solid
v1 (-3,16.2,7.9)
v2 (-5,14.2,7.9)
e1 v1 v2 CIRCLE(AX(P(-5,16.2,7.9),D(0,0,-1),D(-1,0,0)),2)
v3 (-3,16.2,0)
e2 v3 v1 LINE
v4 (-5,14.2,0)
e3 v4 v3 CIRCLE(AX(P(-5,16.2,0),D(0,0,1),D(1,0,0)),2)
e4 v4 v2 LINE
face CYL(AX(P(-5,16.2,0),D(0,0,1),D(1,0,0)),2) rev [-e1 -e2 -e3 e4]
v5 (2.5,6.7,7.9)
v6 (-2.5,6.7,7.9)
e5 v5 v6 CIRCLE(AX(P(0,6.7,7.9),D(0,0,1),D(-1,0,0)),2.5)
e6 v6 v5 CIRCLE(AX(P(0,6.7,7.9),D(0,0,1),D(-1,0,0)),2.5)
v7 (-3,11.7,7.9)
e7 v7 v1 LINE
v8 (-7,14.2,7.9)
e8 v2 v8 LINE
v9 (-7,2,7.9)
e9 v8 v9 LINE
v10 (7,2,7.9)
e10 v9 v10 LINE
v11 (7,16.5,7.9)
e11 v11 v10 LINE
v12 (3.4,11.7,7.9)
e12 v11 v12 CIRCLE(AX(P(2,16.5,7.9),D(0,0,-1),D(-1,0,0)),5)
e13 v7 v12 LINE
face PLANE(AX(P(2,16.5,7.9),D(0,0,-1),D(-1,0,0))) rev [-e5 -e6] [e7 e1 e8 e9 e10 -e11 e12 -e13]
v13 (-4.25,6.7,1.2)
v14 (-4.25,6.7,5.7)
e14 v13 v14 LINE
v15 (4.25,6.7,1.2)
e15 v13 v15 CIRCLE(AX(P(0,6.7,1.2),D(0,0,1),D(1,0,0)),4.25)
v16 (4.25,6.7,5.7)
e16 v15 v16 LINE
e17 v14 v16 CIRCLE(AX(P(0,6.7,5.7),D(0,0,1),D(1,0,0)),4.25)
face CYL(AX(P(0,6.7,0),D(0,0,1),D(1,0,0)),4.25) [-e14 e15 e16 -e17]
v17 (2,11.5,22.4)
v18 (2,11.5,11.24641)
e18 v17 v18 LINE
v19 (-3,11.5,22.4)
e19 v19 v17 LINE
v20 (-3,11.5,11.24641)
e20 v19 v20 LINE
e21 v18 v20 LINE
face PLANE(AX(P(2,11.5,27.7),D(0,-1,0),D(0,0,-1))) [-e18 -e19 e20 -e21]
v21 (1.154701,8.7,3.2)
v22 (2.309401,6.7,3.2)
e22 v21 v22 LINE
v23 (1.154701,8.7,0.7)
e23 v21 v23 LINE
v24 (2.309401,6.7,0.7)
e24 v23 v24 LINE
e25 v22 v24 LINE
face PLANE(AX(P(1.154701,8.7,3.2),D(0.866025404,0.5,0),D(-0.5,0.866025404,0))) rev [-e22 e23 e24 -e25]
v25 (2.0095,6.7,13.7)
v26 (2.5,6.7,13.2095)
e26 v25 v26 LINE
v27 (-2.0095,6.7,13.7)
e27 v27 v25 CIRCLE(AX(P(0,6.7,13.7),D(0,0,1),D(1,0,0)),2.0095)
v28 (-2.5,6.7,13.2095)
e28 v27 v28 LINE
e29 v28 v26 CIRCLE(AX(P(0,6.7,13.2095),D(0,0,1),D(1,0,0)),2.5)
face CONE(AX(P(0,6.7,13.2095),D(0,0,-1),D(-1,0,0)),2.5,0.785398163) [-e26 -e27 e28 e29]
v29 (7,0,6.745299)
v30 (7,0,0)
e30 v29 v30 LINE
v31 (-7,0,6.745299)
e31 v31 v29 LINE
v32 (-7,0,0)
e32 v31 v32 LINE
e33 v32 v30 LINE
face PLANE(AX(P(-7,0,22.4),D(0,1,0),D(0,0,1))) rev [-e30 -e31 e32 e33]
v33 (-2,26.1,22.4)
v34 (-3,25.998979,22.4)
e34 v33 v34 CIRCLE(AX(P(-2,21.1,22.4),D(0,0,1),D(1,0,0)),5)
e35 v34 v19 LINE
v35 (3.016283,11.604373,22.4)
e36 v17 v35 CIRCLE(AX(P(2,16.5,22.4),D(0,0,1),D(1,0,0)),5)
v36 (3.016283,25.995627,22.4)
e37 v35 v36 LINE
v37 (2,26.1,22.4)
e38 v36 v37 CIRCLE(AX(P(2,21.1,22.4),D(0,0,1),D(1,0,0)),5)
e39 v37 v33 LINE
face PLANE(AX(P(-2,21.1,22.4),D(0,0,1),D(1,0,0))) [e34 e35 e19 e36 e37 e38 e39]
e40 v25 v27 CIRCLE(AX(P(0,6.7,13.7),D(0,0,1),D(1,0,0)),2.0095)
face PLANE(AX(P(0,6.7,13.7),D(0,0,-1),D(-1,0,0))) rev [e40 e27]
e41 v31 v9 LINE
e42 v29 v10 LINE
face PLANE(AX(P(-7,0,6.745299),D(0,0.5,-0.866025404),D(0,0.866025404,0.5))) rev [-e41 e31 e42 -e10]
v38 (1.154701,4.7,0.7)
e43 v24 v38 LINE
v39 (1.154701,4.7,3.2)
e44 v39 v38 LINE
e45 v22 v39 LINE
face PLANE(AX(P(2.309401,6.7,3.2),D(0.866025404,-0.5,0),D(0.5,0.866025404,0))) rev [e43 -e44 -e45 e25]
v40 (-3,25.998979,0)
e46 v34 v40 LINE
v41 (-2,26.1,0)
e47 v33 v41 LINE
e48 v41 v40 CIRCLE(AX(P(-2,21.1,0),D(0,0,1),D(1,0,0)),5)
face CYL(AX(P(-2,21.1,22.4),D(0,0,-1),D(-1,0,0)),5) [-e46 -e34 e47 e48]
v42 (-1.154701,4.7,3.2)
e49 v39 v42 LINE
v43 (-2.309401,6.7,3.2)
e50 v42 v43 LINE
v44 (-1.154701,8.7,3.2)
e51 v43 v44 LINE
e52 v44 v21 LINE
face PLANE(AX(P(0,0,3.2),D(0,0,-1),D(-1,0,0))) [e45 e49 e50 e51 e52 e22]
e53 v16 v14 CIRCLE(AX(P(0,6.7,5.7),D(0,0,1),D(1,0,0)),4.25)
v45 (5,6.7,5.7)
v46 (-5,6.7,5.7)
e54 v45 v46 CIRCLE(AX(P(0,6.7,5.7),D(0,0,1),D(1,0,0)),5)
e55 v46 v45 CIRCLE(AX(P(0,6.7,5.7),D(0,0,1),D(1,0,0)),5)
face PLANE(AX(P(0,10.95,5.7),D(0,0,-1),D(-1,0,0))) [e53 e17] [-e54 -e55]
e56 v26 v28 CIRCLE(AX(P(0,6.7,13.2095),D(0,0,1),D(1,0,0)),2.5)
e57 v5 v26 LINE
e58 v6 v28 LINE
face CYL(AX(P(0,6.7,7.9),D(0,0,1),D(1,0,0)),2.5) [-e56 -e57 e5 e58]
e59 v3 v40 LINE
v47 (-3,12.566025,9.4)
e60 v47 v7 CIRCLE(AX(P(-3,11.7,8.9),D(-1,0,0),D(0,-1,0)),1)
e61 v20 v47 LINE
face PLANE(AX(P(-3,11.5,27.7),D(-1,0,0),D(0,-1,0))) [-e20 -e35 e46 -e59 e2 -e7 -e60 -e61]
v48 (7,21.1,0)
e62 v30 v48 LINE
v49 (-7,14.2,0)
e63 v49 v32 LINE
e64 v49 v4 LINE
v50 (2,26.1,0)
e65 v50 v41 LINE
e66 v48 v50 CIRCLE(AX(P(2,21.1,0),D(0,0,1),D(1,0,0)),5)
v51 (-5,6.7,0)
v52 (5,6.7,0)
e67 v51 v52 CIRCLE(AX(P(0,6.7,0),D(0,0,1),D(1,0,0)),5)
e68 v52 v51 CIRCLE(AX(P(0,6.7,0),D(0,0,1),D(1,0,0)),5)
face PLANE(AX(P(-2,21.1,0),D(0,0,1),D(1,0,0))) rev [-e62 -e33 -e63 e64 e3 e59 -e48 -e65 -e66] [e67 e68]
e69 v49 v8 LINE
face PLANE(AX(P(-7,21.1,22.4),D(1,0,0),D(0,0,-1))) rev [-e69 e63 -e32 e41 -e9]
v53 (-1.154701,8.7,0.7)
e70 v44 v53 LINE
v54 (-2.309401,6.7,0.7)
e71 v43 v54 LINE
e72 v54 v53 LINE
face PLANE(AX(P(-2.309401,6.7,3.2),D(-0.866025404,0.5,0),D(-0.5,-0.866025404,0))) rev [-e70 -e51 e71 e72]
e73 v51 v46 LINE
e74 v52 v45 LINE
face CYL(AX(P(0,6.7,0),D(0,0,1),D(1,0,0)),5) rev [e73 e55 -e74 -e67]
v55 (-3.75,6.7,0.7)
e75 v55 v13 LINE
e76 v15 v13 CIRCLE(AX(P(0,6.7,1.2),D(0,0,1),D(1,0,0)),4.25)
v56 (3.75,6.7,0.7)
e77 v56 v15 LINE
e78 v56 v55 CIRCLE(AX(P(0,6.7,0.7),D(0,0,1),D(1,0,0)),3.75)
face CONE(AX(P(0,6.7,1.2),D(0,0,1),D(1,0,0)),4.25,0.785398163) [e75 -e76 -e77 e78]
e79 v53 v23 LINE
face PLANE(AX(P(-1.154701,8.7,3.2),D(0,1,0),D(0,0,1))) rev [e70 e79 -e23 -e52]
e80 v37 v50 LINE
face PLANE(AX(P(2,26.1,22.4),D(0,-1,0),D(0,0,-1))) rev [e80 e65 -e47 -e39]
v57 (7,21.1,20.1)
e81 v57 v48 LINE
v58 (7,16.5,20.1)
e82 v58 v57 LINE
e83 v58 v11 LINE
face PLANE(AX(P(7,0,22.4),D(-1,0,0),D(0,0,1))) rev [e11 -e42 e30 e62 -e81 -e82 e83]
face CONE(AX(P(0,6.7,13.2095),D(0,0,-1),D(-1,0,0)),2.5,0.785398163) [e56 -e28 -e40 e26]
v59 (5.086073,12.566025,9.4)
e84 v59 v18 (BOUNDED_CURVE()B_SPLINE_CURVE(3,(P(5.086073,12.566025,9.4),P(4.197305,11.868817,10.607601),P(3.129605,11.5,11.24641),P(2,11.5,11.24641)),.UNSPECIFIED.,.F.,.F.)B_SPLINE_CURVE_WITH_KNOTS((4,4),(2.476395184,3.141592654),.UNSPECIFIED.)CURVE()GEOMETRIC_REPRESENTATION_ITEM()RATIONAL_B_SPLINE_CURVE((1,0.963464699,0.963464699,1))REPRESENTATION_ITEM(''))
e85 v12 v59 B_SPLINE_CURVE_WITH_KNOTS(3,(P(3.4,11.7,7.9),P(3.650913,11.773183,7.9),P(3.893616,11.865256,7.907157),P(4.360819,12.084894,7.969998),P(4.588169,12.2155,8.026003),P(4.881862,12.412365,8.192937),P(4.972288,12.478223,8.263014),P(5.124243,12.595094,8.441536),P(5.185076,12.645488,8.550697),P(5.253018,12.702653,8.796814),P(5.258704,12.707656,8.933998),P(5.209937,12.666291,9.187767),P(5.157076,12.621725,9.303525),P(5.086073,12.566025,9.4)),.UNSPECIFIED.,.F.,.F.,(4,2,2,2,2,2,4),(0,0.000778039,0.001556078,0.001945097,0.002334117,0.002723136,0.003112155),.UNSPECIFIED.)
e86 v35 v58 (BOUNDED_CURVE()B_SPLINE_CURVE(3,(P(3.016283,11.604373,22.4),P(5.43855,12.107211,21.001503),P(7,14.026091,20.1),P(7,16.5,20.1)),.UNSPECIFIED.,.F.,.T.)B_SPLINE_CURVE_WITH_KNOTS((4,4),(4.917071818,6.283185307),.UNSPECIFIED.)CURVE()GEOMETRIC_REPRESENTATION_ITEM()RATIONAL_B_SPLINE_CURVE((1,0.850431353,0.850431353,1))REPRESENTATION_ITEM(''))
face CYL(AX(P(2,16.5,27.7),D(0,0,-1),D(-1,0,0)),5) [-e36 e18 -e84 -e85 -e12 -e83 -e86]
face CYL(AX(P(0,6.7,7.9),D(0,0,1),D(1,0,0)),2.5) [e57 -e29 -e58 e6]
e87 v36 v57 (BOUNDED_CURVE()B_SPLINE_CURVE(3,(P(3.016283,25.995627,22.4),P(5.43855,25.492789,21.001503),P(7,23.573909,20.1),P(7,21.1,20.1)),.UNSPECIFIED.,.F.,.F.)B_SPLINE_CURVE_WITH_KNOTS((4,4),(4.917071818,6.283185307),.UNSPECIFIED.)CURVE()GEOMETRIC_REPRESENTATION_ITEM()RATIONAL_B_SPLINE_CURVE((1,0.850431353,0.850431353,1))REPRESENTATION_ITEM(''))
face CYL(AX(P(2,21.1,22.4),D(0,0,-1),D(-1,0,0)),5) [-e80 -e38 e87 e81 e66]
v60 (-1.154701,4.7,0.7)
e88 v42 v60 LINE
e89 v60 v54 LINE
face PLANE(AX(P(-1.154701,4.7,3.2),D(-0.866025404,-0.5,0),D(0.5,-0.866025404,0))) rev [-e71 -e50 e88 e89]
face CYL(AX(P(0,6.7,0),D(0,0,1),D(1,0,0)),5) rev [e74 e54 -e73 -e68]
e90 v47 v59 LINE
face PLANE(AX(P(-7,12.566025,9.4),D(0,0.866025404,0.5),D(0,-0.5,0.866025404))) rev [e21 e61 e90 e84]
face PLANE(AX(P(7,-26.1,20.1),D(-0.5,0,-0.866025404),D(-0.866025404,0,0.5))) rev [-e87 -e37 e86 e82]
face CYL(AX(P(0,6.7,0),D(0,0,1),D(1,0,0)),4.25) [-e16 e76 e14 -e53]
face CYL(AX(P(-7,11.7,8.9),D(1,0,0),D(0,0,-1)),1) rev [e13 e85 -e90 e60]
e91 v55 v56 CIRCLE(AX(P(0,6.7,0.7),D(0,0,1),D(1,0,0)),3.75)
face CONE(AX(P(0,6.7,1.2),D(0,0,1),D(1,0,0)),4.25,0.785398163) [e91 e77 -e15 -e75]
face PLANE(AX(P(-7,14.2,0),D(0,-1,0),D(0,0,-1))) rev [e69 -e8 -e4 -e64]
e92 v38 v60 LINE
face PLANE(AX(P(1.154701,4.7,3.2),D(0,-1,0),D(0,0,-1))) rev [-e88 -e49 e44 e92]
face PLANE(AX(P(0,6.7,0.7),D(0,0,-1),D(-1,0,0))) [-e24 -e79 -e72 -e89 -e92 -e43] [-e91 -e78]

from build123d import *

# Parameters (mm, degrees)
BOSS_EXTRUDE1_DEPTH     = 22.4
CUT_EXTRUDE1_DEPTH      = 7
CUT_EXTRUDE1_DEPTH_BACK = 7
CUT_EXTRUDE2_DEPTH      = 19.8
CUT_EXTRUDE3_DEPTH      = 2.5
CUT_EXTRUDE4_DEPTH      = 5.925
CUT_EXTRUDE4_DEPTH_BACK = 5.925
CUT_EXTRUDE5_DEPTH      = 7
CUT_EXTRUDE5_DEPTH_BACK = 7
CUT_EXTRUDE6_DEPTH      = 26.1
CUT_EXTRUDE6_DEPTH_BACK = 26.1


with BuildPart() as part:
    # Sketch1 → Boss-Extrude1 (new body)
    with BuildSketch(Plane.XY):
        with BuildLine():
            Line((-7, 21.1), (-7, 0))
            Line((-7, 0), (7, 0))
            Line((7, 0), (7, 21.1))
            ThreePointArc((7, 21.1), (5.535533906, 24.635533906), (2, 26.1))
            Line((2, 26.1), (-2, 26.1))
            ThreePointArc((-2, 26.1), (-5.535533906, 24.635533906), (-7, 21.1))
        make_face()
    extrude(amount=BOSS_EXTRUDE1_DEPTH)

    # Sketch2 → Cut-Extrude1 (cut, two sides: drawn at the far end of the back side and taken through both)
    with BuildSketch(Plane(origin=(0, 0, 0), x_dir=(0, 0, -1), z_dir=(1, 0, 0)).offset(-CUT_EXTRUDE1_DEPTH_BACK)):
        Polygon((-7.9, 2), (-7.9, 0), (-6.745299462, 0), align=None)
    extrude(amount=CUT_EXTRUDE1_DEPTH + CUT_EXTRUDE1_DEPTH_BACK, mode=Mode.SUBTRACT)

    # Sketch4 → Cut-Extrude2 (cut)
    with BuildSketch(Plane.XY.offset(7.9)):
        with BuildLine():
            Line((-7, 26.1), (-7, 0))
            Line((-7, 0), (9, 0))
            Line((9, 0), (9, 16.5))
            Line((9, 16.5), (7, 16.5))
            ThreePointArc((7, 16.5), (5.535533906, 12.964466094), (2, 11.5))
            Line((2, 11.5), (-3, 11.5))
            Line((-3, 11.5), (-3, 26.1))
            Line((-3, 26.1), (-7, 26.1))
        make_face()
    extrude(amount=CUT_EXTRUDE2_DEPTH, mode=Mode.SUBTRACT)

    # Sketch3 → Cut-Revolve1 (revolve, cut)
    with BuildSketch(Plane(origin=(0, 0, 0), x_dir=(0, 0, -1), z_dir=(1, 0, 0)), mode=Mode.PRIVATE) as cut_revolve1_sk:
        Polygon((-0.7, 6.7), (-0.7, 10.45), (-1.2, 10.95), (-5.7, 10.95), (-5.7, 11.7), (0, 11.7), (0, 6.7), align=None)
    revolve(cut_revolve1_sk.sketch.rotate(Axis((0, 6.7, 0), (0, 0, 1)), 270), axis=Axis((0, 6.7, 0), (0, 0, 1)), mode=Mode.SUBTRACT)

    # Sketch5 → Cut-Extrude3 (cut)
    with BuildSketch(Plane(origin=(0, 0, 0.7), x_dir=(-1, 0, 0), z_dir=(0, 0, -1))):
        Polygon((1.154700538, 4.7), (2.309401077, 6.7), (1.154700538, 8.7), (-1.154700538, 8.7), (-2.309401077, 6.7), (-1.154700538, 4.7), align=None)
    extrude(amount=-CUT_EXTRUDE3_DEPTH, mode=Mode.SUBTRACT)

    # Sketch6 → Cut-Extrude4 (cut, two sides: drawn at the far end of the back side and taken through both)
    with BuildSketch(Plane.XY.offset(5.925).offset(-CUT_EXTRUDE4_DEPTH_BACK)):
        with BuildLine():
            Line((-7, 14.2), (-5, 14.2))
            ThreePointArc((-5, 14.2), (-3.585786438, 14.785786438), (-3, 16.2))
            Line((-3, 16.2), (-3, 26.1))
            Line((-3, 26.1), (-7, 26.1))
            Line((-7, 26.1), (-7, 14.2))
        make_face()
    extrude(amount=CUT_EXTRUDE4_DEPTH + CUT_EXTRUDE4_DEPTH_BACK, mode=Mode.SUBTRACT)

    # Sketch7 → Cut-Extrude5 (cut, two sides: drawn at the far end of the back side and taken through both)
    with BuildSketch(Plane(origin=(0, 0, 0), x_dir=(0, 0, -1), z_dir=(1, 0, 0)).offset(-CUT_EXTRUDE5_DEPTH_BACK)):
        with BuildLine():
            Line((-11.419615242, 11.4), (-7.9, 11.4))
            Line((-7.9, 11.4), (-7.9, 11.7))
            ThreePointArc((-7.9, 11.7), (-8.4, 12.566025404), (-9.4, 12.566025404))
            Line((-9.4, 12.566025404), (-11.419615242, 11.4))
        make_face()
    extrude(amount=CUT_EXTRUDE5_DEPTH + CUT_EXTRUDE5_DEPTH_BACK, mode=Mode.SUBTRACT)

    # Sketch8 → Cut-Extrude6 (cut, two sides: drawn at the far end of the back side and taken through both)
    with BuildSketch(Plane(origin=(0, 0, 0), x_dir=(1, 0, 0), z_dir=(0, 1, 0)).offset(-CUT_EXTRUDE6_DEPTH_BACK)):
        Polygon((3.016283143, -22.4), (7, -22.4), (7, -20.1), align=None)
    extrude(amount=CUT_EXTRUDE6_DEPTH + CUT_EXTRUDE6_DEPTH_BACK, mode=Mode.SUBTRACT)

    # Sketch9 → Revolve1 (revolve)
    with BuildSketch(Plane(origin=(0, 0, 0), x_dir=(0, 0, -1), z_dir=(1, 0, 0)), mode=Mode.PRIVATE) as revolve1_sk:
        Polygon((-13.7, 6.7), (-13.7, 8.7095), (-13.2095, 9.2), (-7.9, 9.2), (-7.9, 6.7), align=None)
    revolve(revolve1_sk.sketch.rotate(Axis((0, 6.7, 7.9), (0, 0, 1)), 270), axis=Axis((0, 6.7, 7.9), (0, 0, 1)))


solid = part.part
